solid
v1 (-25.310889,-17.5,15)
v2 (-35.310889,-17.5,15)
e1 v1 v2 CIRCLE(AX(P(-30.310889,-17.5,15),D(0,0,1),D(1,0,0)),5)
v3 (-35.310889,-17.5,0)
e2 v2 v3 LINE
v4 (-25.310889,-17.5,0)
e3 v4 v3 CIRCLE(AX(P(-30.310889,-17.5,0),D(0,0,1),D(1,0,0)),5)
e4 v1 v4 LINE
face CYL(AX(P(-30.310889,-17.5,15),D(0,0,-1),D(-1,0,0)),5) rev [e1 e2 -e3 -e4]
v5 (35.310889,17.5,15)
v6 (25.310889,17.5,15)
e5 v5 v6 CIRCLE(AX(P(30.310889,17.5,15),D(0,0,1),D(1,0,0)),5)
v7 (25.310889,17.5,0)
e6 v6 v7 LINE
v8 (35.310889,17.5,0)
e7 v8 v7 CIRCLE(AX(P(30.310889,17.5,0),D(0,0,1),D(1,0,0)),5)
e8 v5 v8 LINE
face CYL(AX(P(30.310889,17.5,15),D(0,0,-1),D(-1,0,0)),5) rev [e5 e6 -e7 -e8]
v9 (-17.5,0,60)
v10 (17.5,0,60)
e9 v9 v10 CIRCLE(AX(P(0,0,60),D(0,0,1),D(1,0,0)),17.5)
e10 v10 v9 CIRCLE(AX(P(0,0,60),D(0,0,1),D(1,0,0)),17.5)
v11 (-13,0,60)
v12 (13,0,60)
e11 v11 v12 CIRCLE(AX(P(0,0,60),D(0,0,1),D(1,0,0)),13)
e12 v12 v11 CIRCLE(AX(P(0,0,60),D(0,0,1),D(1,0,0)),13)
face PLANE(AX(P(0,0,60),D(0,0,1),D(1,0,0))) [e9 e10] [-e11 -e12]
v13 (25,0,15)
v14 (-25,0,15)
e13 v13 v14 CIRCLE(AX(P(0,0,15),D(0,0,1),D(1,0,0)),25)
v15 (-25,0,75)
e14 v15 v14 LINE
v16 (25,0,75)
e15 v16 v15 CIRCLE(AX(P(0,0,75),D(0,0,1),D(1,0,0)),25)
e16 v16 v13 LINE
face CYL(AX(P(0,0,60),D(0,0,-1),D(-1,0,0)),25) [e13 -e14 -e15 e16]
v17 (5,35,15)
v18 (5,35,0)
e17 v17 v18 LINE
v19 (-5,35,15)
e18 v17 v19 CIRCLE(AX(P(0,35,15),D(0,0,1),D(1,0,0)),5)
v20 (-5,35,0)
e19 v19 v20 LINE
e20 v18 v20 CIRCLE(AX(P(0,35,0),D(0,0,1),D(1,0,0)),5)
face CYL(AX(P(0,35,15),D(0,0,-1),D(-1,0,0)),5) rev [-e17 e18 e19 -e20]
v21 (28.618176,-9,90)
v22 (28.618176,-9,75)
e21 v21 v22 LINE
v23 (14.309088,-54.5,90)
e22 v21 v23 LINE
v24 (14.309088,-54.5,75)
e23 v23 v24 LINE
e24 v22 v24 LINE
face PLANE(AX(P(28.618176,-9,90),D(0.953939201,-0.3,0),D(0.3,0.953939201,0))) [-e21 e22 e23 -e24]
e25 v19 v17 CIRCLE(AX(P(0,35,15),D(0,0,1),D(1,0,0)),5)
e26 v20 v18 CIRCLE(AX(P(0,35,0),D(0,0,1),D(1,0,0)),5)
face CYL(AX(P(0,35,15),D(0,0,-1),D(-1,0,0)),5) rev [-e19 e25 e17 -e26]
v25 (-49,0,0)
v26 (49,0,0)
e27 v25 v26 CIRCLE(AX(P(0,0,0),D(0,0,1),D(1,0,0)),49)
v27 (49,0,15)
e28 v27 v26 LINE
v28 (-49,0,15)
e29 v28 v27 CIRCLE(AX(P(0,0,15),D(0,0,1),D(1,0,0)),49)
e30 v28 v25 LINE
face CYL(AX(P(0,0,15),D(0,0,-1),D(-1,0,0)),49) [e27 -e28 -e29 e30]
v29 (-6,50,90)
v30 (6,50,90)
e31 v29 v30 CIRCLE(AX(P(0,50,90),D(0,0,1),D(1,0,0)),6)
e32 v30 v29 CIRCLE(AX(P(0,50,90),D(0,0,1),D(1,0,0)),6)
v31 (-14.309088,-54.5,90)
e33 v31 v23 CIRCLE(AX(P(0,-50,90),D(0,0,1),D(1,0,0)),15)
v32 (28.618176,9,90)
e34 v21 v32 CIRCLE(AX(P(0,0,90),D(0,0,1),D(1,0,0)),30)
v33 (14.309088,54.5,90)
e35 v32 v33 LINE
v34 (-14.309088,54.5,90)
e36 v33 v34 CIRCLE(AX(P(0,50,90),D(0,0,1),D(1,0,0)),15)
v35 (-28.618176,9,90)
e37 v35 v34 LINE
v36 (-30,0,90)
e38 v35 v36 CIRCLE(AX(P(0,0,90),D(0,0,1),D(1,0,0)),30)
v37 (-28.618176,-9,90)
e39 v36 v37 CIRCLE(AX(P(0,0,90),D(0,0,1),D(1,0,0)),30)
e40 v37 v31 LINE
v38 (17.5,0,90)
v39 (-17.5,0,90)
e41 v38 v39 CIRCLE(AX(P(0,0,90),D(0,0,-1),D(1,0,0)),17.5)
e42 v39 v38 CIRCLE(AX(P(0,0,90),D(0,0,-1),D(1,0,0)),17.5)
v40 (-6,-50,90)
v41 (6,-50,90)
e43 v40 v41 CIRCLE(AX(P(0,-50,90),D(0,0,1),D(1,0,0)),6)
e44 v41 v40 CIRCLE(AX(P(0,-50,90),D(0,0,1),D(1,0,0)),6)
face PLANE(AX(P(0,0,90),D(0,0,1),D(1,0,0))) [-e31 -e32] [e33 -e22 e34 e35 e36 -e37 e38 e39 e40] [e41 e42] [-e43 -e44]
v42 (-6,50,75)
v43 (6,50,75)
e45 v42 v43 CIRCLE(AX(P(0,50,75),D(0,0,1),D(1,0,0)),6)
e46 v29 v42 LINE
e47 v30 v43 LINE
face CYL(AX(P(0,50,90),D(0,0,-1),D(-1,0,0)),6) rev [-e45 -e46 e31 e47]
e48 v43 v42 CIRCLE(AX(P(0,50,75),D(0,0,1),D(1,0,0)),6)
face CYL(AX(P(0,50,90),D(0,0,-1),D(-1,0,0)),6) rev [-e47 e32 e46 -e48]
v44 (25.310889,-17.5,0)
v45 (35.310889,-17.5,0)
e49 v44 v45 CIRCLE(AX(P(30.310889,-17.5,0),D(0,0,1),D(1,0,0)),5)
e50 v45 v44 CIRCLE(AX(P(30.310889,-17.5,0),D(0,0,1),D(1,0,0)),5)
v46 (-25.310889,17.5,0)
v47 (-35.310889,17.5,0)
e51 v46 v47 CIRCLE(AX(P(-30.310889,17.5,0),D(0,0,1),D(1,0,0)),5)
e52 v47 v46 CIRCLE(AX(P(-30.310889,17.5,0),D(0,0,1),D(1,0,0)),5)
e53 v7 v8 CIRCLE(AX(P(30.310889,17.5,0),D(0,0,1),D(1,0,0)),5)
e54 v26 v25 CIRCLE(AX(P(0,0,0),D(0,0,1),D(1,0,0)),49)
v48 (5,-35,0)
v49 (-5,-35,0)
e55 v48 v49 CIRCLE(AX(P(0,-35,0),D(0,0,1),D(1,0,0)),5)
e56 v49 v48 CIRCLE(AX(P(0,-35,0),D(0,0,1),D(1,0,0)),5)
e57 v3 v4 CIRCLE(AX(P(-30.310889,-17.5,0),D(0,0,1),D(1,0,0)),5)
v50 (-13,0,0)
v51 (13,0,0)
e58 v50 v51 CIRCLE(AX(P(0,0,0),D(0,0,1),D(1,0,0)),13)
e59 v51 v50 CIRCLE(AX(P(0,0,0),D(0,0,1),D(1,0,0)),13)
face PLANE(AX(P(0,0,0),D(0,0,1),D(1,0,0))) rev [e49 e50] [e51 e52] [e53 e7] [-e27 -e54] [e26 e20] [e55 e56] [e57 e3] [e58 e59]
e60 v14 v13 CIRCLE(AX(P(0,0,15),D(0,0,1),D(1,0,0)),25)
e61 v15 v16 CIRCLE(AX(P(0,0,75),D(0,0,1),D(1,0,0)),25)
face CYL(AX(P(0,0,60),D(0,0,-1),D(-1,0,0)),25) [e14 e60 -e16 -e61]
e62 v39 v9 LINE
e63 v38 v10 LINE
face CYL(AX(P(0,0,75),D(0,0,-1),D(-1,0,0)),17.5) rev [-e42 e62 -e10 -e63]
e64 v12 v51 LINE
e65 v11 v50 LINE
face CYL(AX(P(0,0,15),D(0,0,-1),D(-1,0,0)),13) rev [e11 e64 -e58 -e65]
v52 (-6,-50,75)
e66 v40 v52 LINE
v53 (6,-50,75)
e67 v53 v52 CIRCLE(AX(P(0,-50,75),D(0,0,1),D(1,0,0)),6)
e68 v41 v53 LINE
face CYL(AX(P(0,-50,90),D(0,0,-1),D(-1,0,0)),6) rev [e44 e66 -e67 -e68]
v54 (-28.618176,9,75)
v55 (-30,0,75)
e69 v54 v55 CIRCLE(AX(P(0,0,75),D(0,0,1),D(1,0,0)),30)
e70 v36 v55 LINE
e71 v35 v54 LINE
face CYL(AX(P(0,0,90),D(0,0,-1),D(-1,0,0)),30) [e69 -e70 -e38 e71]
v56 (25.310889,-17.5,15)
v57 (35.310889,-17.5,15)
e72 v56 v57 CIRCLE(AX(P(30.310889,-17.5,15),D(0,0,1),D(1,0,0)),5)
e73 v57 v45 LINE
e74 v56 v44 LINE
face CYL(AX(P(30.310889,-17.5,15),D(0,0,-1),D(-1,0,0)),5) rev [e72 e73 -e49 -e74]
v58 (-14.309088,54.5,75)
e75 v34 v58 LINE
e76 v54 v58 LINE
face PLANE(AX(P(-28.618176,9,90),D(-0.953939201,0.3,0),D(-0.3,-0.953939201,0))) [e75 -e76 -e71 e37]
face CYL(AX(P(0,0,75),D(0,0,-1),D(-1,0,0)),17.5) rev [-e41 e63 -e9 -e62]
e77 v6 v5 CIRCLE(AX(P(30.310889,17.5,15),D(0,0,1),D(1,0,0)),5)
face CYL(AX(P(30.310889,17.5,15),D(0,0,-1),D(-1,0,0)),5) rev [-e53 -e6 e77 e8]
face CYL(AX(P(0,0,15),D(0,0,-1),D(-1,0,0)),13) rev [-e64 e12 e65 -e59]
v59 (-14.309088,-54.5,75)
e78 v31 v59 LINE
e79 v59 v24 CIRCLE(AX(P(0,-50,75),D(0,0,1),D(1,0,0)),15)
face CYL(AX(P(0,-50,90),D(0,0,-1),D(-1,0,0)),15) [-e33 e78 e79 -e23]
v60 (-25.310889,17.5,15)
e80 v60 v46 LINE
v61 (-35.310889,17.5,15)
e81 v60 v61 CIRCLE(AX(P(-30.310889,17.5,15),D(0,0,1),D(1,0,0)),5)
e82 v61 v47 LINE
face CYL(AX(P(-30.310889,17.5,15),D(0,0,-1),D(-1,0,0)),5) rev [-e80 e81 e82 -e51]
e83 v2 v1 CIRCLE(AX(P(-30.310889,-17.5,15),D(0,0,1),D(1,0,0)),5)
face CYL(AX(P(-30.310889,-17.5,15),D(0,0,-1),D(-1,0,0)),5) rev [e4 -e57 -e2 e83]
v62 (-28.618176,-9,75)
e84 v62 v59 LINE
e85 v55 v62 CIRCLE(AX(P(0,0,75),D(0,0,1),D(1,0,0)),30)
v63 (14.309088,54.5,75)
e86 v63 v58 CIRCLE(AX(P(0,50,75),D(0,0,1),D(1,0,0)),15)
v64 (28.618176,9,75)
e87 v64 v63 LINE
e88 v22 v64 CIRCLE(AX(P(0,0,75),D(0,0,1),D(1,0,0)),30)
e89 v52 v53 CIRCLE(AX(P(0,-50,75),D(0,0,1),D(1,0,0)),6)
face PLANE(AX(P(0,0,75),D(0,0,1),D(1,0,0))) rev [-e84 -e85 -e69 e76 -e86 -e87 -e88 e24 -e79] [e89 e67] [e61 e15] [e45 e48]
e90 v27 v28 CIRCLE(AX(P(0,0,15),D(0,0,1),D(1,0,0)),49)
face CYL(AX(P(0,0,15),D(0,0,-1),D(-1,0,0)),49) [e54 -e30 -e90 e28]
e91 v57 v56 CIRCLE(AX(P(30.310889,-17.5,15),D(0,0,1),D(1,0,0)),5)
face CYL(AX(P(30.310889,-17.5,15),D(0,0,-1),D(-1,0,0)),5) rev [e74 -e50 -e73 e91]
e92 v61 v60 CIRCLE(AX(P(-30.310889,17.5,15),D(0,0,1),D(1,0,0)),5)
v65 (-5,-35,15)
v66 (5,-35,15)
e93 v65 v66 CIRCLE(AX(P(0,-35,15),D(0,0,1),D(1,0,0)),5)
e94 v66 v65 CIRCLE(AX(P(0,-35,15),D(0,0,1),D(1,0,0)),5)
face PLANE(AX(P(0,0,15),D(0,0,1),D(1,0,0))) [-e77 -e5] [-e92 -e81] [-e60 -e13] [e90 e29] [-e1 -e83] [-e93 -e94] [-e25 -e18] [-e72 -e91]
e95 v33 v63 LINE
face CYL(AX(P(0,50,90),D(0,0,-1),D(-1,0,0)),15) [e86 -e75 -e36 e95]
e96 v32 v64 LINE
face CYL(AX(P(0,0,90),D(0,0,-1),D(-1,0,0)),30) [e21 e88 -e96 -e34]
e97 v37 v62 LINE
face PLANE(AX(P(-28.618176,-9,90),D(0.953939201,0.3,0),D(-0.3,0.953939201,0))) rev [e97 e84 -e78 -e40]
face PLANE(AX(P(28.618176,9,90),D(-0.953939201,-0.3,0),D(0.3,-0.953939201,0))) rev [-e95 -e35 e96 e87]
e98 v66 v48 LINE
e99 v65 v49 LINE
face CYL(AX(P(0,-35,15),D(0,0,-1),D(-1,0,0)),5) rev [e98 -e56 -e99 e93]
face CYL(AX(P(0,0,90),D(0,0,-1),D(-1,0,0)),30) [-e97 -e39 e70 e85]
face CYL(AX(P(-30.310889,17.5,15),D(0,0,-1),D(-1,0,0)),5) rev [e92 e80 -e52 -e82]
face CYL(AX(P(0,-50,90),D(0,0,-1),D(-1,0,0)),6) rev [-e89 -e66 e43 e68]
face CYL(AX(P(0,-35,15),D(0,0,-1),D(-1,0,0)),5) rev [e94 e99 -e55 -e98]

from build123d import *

# Parameters (mm, degrees)
ROUND_FLANGE_SKETCH_R       = 49
ROUND_FLANGE_SKETCH_R_2     = 13
ROUND_FLANGE_SKETCH_R_3     = 5
ROUND_FLANGE_98_6X_10_DEPTH = 15
TUBE_SKETCH_R               = 25
TUBE_SKETCH_R_2             = 13
TUBE_50_BORE_26_DEPTH       = 45
COLLAR_SKETCH_R             = 25
COLLAR_SKETCH_R_2           = 17.5
COLLAR_DEPTH                = 15
OVAL_FLANGE_SKETCH_R        = 25
OVAL_FLANGE_SKETCH_R_2      = 17.5
OVAL_FLANGE_SKETCH_R_3      = 15
OVAL_FLANGE_SKETCH_R_4      = 6
OVAL_FLANGE_2X_12_DEPTH     = 15


with BuildPart() as part:
    # Round Flange Sketch → Round Flange Ø98 6xØ10 (new body)
    with BuildSketch(Plane.XY):
        Circle(ROUND_FLANGE_SKETCH_R)
        Circle(ROUND_FLANGE_SKETCH_R_2, mode=Mode.SUBTRACT)
        with Locations((0, 35)):
            Circle(ROUND_FLANGE_SKETCH_R_3, mode=Mode.SUBTRACT)
        with Locations((30.310889132, 17.5)):
            Circle(ROUND_FLANGE_SKETCH_R_3, mode=Mode.SUBTRACT)
        with Locations((30.310889132, -17.5)):
            Circle(ROUND_FLANGE_SKETCH_R_3, mode=Mode.SUBTRACT)
        with Locations((0, -35)):
            Circle(ROUND_FLANGE_SKETCH_R_3, mode=Mode.SUBTRACT)
        with Locations((-30.310889132, -17.5)):
            Circle(ROUND_FLANGE_SKETCH_R_3, mode=Mode.SUBTRACT)
        with Locations((-30.310889132, 17.5)):
            Circle(ROUND_FLANGE_SKETCH_R_3, mode=Mode.SUBTRACT)
    extrude(amount=ROUND_FLANGE_98_6X_10_DEPTH)

    # Tube Sketch → Tube Ø50 Bore Ø26 (add)
    with BuildSketch(Plane.XY.offset(15)):
        with Locations(Location((0, 0, 0), (0, 0, 180))):
            Circle(TUBE_SKETCH_R)
        Circle(TUBE_SKETCH_R_2, mode=Mode.SUBTRACT)
    extrude(amount=TUBE_50_BORE_26_DEPTH)

    # Collar Sketch → Collar (add)
    with BuildSketch(Plane.XY.offset(60)):
        with Locations(Location((0, 0, 0), (0, 0, 180))):
            Circle(COLLAR_SKETCH_R)
        Circle(COLLAR_SKETCH_R_2, mode=Mode.SUBTRACT)
    extrude(amount=COLLAR_DEPTH)

    # Oval Flange Sketch → Oval Flange 2xØ12 (add)
    # profile 1 of 4: a face of its own
    with BuildSketch(Plane.XY.offset(75)):
        with BuildLine():
            Line((-14.309088021, 54.5), (-28.618176043, 9))
            ThreePointArc((-28.618176043, 9), (-30, 0), (-28.618176043, -9))
            Line((-28.618176043, -9), (-14.309088021, -54.5))
            ThreePointArc((-14.309088021, -54.5), (-2.276365489, -35.173734113), (15, -50))
            ThreePointArc((15, -50), (14.826265887, -52.276365489), (14.309088021, -54.5))
            Line((14.309088021, -54.5), (28.618176043, -9))
            ThreePointArc((28.618176043, -9), (30, 0), (28.618176043, 9))
            Line((28.618176043, 9), (14.309088021, 54.5))
            ThreePointArc((14.309088021, 54.5), (14.826265887, 52.276365489), (15, 50))
            ThreePointArc((15, 50), (-2.276365489, 35.173734113), (-14.309088021, 54.5))
        make_face()
        with Locations(Location((0, 0, 0), (0, 0, 180))):
            Circle(OVAL_FLANGE_SKETCH_R, mode=Mode.SUBTRACT)
    # profile 2 of 4: a face of its own
    with BuildSketch(Plane.XY.offset(75)):
        with Locations(Location((0, 0, 0), (0, 0, 180))):
            Circle(OVAL_FLANGE_SKETCH_R)
        Circle(OVAL_FLANGE_SKETCH_R_2, mode=Mode.SUBTRACT)
    # profile 3 of 4: a face of its own
    with BuildSketch(Plane.XY.offset(75)):
        with Locations((0, 50)):
            Circle(OVAL_FLANGE_SKETCH_R_3)
        with Locations((0, 50)):
            Circle(OVAL_FLANGE_SKETCH_R_4, mode=Mode.SUBTRACT)
    # profile 4 of 4: a face of its own
    with BuildSketch(Plane.XY.offset(75)):
        with Locations((0, -50)):
            Circle(OVAL_FLANGE_SKETCH_R_3)
        with Locations((0, -50)):
            Circle(OVAL_FLANGE_SKETCH_R_4, mode=Mode.SUBTRACT)
    extrude(amount=OVAL_FLANGE_2X_12_DEPTH)


solid = part.part
